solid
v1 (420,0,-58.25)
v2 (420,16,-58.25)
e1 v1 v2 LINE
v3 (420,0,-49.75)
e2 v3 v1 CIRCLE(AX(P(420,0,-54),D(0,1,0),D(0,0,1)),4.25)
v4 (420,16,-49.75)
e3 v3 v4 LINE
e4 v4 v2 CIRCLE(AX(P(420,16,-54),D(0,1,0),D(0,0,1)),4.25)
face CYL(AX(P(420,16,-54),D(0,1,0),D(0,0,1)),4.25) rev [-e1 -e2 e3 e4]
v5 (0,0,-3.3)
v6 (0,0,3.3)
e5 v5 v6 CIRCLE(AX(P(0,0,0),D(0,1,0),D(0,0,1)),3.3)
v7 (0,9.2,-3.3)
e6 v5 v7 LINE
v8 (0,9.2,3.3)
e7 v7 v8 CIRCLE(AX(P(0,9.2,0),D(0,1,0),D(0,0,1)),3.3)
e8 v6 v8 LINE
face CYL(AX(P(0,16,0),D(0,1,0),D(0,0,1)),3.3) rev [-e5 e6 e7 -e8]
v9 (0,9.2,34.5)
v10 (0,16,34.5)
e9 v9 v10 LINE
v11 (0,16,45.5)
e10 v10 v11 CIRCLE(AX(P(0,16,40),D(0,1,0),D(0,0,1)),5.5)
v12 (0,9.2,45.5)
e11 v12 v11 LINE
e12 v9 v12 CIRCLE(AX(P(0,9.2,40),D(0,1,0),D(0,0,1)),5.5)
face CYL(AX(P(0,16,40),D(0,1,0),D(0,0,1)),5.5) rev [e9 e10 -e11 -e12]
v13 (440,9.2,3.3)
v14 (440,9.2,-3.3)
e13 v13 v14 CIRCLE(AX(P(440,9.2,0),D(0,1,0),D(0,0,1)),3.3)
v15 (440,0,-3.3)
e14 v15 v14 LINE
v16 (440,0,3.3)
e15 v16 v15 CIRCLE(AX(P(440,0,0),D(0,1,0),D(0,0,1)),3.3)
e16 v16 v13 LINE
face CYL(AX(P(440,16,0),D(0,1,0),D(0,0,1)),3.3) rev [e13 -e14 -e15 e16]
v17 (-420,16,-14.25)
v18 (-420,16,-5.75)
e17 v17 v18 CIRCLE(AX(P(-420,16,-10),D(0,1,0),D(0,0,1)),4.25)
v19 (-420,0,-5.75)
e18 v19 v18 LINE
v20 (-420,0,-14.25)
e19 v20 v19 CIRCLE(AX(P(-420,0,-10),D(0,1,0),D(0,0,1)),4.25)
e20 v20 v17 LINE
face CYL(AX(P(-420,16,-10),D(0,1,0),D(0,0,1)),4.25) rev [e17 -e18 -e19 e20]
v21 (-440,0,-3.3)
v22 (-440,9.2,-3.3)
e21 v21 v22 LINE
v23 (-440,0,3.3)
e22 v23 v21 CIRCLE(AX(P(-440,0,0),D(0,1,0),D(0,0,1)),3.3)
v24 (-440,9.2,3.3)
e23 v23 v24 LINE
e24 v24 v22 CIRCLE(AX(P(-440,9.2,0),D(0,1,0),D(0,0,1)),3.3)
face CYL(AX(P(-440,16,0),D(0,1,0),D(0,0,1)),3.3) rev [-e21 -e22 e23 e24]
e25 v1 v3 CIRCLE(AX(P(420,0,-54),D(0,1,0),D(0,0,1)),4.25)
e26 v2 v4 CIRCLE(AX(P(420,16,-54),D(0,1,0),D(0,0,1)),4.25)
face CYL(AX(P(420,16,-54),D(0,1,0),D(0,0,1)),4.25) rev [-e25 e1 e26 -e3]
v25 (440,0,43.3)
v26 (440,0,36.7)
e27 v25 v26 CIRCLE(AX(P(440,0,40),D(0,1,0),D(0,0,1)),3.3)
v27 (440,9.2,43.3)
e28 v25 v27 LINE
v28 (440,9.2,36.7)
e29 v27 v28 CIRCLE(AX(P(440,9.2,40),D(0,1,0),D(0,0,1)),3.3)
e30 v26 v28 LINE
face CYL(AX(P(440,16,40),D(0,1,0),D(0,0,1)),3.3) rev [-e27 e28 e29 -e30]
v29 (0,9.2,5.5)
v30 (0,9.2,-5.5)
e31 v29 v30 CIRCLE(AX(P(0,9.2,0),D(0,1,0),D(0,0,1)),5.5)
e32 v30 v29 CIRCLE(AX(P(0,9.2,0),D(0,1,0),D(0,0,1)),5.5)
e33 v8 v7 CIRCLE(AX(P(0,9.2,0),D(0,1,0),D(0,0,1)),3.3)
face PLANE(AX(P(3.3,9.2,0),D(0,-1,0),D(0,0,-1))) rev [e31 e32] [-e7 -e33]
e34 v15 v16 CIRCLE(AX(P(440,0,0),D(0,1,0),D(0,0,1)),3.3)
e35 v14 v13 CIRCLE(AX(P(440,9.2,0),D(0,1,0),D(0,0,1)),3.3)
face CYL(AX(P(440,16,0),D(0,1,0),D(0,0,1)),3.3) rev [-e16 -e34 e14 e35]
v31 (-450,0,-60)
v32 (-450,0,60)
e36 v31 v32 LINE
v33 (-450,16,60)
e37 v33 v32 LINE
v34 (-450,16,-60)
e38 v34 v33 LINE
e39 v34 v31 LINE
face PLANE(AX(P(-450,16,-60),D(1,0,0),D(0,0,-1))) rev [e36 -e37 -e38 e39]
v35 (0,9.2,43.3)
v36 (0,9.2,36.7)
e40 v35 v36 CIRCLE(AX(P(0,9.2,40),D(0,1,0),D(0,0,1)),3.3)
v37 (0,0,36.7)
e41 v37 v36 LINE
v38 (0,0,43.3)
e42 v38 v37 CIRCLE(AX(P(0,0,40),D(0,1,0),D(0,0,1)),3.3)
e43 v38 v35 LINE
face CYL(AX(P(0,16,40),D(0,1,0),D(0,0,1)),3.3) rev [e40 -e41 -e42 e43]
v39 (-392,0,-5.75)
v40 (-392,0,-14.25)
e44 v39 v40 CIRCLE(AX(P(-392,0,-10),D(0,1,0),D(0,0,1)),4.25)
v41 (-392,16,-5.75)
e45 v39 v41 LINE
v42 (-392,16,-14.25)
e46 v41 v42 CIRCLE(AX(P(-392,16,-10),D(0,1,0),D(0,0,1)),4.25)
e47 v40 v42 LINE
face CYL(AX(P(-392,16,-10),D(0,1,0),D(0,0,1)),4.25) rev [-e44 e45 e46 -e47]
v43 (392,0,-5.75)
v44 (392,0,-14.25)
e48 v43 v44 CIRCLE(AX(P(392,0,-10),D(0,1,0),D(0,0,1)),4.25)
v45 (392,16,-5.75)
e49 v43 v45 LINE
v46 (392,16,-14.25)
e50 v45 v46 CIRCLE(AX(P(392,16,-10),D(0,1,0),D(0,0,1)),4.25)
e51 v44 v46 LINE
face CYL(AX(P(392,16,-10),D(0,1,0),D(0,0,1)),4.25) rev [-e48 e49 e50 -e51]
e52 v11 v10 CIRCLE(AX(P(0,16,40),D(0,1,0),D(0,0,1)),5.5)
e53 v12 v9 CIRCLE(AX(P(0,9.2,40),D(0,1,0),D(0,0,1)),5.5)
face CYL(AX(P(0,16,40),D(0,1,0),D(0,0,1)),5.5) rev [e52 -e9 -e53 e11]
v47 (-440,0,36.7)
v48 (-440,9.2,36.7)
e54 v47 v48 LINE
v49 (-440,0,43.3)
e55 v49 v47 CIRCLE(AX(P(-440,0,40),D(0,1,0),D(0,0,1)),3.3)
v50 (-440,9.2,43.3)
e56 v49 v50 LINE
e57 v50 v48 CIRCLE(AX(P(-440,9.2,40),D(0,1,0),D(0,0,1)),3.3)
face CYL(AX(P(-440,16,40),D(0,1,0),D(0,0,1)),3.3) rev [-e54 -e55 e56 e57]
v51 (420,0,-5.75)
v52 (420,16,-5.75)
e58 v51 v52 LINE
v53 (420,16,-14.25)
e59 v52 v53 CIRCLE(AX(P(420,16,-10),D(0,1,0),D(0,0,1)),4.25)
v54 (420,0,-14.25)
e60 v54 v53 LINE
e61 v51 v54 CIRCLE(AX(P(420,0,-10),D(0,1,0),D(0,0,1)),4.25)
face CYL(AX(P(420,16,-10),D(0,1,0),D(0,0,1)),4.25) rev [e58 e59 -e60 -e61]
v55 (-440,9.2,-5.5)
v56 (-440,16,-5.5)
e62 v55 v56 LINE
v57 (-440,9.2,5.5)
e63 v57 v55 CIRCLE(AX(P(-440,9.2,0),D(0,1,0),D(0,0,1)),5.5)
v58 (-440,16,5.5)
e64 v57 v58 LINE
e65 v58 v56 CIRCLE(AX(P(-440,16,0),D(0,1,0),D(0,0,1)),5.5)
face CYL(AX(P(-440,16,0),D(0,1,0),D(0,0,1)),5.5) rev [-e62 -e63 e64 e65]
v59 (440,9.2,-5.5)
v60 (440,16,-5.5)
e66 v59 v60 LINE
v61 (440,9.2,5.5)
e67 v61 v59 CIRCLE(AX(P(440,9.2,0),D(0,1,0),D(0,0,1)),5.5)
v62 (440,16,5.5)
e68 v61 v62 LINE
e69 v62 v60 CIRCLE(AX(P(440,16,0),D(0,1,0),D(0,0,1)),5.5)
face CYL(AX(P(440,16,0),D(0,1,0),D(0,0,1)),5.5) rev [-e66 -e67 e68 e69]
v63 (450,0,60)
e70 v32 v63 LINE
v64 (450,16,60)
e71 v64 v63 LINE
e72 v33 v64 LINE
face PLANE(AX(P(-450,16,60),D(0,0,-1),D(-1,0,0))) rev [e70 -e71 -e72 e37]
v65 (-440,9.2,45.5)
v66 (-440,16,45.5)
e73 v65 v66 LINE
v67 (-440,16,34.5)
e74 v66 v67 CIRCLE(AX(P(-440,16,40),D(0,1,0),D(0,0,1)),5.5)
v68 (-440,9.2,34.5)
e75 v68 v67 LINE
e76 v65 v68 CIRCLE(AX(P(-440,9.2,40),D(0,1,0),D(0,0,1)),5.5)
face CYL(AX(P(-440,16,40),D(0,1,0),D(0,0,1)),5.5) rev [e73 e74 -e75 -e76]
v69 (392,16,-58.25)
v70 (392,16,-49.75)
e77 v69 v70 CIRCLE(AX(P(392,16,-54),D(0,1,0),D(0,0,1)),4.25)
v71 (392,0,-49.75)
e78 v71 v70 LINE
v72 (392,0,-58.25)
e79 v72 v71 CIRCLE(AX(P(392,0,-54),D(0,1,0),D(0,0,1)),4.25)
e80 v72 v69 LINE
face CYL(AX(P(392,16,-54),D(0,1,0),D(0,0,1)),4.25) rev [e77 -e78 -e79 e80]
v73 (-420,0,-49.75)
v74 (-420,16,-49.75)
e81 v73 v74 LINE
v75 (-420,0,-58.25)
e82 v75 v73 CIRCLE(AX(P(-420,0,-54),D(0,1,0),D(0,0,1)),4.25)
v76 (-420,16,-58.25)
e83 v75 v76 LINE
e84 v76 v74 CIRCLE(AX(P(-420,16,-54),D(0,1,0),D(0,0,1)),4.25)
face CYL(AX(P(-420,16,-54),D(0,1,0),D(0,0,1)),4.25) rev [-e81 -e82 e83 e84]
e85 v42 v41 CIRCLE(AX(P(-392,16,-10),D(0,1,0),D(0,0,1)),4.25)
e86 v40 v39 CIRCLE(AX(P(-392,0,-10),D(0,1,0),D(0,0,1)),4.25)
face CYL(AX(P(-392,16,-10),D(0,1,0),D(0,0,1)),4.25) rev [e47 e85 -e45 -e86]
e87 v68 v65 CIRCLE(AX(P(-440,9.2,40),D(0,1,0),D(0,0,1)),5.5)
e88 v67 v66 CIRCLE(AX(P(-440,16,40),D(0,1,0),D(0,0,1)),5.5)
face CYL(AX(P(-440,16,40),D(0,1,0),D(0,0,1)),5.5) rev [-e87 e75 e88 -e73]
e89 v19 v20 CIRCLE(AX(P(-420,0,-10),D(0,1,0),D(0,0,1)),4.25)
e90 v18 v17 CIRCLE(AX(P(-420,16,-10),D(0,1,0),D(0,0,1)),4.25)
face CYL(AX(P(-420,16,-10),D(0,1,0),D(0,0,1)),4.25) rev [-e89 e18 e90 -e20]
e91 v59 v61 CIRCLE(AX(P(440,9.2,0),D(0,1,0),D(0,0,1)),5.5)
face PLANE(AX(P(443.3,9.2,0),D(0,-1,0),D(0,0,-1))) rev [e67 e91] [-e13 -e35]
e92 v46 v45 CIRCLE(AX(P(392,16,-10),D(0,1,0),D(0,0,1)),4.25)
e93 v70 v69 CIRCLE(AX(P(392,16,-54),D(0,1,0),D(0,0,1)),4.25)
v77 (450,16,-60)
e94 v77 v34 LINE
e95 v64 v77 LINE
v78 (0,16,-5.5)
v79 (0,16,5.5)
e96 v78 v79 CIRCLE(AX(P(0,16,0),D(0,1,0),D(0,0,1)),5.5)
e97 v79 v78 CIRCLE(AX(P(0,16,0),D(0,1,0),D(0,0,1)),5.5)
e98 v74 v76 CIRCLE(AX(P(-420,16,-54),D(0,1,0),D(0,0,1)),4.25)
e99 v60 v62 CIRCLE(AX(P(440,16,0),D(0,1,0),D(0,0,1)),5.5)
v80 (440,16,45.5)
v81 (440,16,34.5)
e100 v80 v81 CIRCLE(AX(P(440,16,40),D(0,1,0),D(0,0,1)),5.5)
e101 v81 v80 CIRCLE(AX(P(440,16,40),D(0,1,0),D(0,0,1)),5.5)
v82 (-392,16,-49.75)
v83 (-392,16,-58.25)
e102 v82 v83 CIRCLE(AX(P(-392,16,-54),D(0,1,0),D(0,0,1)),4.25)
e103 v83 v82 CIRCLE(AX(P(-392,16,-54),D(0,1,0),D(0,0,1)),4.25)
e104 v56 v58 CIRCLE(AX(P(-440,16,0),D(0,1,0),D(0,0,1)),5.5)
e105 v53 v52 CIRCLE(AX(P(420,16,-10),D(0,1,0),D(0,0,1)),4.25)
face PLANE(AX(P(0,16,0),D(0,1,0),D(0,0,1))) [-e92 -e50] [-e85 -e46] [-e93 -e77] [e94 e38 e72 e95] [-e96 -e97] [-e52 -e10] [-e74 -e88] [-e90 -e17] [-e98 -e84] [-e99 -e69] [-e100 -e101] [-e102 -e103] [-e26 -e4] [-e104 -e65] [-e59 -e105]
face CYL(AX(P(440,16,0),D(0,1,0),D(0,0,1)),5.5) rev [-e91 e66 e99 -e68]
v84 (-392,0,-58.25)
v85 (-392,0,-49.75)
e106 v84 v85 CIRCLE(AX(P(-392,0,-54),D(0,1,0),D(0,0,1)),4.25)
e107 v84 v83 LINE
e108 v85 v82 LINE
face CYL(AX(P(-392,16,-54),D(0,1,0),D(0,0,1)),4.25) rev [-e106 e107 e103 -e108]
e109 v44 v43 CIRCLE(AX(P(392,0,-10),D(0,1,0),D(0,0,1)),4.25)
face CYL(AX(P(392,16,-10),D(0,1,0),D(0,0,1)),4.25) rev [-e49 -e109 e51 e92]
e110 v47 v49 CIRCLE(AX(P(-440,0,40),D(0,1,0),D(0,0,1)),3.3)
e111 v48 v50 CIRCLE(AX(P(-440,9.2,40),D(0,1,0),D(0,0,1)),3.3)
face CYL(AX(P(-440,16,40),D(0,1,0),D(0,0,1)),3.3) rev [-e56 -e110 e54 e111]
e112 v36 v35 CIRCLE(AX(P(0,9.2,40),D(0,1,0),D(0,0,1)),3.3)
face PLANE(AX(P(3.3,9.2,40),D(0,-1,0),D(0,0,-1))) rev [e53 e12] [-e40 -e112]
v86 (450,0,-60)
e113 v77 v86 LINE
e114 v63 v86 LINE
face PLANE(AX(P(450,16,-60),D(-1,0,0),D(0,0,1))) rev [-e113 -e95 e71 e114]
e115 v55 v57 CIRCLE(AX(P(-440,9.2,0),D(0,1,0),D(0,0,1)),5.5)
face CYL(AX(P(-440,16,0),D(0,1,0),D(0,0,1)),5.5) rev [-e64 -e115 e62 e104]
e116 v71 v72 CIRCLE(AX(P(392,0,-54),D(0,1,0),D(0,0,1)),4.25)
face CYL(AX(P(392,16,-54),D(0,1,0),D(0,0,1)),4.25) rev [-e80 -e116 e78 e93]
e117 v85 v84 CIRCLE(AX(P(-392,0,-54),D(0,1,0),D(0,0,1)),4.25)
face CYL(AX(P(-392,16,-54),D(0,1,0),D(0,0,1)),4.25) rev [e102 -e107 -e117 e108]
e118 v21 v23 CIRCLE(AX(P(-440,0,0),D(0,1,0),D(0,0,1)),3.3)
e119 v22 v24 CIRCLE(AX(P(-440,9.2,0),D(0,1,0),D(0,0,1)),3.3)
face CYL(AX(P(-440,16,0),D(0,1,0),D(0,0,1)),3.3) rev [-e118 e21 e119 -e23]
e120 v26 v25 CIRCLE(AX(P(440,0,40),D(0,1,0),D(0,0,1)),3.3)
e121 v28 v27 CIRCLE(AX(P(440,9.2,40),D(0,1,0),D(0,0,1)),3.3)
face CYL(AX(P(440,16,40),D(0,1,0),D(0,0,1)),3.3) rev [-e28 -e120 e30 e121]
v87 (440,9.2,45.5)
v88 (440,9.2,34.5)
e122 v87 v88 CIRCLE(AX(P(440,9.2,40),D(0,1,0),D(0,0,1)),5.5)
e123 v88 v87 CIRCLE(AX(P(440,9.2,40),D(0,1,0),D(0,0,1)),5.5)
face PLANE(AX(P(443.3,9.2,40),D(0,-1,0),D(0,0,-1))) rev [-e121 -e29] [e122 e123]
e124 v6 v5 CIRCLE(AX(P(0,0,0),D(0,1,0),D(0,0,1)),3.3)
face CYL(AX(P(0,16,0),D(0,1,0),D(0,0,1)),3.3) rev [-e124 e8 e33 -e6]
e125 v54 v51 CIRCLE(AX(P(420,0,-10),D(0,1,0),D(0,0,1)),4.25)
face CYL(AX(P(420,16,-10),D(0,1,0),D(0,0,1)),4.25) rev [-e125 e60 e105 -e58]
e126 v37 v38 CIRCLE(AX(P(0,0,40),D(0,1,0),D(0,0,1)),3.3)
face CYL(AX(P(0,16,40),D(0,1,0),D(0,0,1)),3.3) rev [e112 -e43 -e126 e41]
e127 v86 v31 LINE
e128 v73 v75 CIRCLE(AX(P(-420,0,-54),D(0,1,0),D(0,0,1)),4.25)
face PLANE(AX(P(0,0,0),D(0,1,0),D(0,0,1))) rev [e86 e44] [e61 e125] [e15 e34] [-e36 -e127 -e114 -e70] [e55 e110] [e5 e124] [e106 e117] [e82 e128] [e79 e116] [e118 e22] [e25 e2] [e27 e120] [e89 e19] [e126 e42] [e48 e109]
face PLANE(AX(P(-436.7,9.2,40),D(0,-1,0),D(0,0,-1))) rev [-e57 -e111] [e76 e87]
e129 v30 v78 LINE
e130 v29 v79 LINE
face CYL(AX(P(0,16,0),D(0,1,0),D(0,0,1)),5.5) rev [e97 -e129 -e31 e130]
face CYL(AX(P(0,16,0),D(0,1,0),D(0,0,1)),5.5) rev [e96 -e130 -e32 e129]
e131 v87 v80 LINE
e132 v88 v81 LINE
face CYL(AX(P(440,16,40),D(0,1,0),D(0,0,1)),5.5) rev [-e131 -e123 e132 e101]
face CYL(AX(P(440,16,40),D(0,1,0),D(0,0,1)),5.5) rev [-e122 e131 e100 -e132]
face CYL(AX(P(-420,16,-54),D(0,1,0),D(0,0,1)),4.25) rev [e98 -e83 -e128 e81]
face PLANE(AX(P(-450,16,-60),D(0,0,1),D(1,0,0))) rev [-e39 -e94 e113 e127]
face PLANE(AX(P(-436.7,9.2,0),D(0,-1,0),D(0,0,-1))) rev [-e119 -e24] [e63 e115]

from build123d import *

# Parameters (mm, degrees)
SKETCH_1_W                = 900
SKETCH_1_H                = 120
EXTRUDE_1_DEPTH           = 16
HOLE_WIZARD_8_5_8_5_1_D   = 8.5
HOLE_WIZARD_1_D           = 6.6
HOLE_WIZARD_1_CBORE_D     = 11
HOLE_WIZARD_1_CBORE_DEPTH = 6.8
PATTERN_LINEAR_1_COUNT    = 3
PATTERN_LINEAR_1_PITCH    = 440


with BuildPart() as part:
    # 草图1 → 凸台-拉伸1 (new body)
    with BuildSketch(Plane(origin=(0, 0, 0), x_dir=(1, 0, 0), z_dir=(0, 1, 0))):
        Rectangle(SKETCH_1_W, SKETCH_1_H)
    extrude(amount=EXTRUDE_1_DEPTH)

    # Ø8.5 (8.5) 直径孔1 (through all)
    with Locations(Plane(origin=(0, 16, 0), x_dir=(1, 0, 0), z_dir=(0, 1, 0))):
        with Locations((392, 54), (420, 54), (392, 10), (420, 10)):
            hole_wizard_8_5_8_5_1 = Hole(HOLE_WIZARD_8_5_8_5_1_D / 2)

    # 打孔尺寸(%根据)内六角圆柱头螺钉的类型1 (through all)
    with Locations(Plane(origin=(0, 16, 0), x_dir=(1, 0, 0), z_dir=(0, 1, 0))):
        with Locations((-440, 0), (-440, -40)):
            hole_wizard_1 = CounterBoreHole(HOLE_WIZARD_1_D / 2, HOLE_WIZARD_1_CBORE_D / 2, HOLE_WIZARD_1_CBORE_DEPTH)

    # 阵列(线性)1: 打孔尺寸(%根据)内六角圆柱头螺钉的类型1 ×3
    with Locations(*[(i * PATTERN_LINEAR_1_PITCH, 0, 0) for i in range(1, PATTERN_LINEAR_1_COUNT)]):
        add(hole_wizard_1, mode=Mode.SUBTRACT)

    # 镜向1: Ø8.5 (8.5) 直径孔1 across plane
    add(hole_wizard_8_5_8_5_1.mirror(Plane(origin=(0, 0, 0), x_dir=(0, 0, 1), z_dir=(1, 0, 0))), mode=Mode.SUBTRACT)


solid = part.part
